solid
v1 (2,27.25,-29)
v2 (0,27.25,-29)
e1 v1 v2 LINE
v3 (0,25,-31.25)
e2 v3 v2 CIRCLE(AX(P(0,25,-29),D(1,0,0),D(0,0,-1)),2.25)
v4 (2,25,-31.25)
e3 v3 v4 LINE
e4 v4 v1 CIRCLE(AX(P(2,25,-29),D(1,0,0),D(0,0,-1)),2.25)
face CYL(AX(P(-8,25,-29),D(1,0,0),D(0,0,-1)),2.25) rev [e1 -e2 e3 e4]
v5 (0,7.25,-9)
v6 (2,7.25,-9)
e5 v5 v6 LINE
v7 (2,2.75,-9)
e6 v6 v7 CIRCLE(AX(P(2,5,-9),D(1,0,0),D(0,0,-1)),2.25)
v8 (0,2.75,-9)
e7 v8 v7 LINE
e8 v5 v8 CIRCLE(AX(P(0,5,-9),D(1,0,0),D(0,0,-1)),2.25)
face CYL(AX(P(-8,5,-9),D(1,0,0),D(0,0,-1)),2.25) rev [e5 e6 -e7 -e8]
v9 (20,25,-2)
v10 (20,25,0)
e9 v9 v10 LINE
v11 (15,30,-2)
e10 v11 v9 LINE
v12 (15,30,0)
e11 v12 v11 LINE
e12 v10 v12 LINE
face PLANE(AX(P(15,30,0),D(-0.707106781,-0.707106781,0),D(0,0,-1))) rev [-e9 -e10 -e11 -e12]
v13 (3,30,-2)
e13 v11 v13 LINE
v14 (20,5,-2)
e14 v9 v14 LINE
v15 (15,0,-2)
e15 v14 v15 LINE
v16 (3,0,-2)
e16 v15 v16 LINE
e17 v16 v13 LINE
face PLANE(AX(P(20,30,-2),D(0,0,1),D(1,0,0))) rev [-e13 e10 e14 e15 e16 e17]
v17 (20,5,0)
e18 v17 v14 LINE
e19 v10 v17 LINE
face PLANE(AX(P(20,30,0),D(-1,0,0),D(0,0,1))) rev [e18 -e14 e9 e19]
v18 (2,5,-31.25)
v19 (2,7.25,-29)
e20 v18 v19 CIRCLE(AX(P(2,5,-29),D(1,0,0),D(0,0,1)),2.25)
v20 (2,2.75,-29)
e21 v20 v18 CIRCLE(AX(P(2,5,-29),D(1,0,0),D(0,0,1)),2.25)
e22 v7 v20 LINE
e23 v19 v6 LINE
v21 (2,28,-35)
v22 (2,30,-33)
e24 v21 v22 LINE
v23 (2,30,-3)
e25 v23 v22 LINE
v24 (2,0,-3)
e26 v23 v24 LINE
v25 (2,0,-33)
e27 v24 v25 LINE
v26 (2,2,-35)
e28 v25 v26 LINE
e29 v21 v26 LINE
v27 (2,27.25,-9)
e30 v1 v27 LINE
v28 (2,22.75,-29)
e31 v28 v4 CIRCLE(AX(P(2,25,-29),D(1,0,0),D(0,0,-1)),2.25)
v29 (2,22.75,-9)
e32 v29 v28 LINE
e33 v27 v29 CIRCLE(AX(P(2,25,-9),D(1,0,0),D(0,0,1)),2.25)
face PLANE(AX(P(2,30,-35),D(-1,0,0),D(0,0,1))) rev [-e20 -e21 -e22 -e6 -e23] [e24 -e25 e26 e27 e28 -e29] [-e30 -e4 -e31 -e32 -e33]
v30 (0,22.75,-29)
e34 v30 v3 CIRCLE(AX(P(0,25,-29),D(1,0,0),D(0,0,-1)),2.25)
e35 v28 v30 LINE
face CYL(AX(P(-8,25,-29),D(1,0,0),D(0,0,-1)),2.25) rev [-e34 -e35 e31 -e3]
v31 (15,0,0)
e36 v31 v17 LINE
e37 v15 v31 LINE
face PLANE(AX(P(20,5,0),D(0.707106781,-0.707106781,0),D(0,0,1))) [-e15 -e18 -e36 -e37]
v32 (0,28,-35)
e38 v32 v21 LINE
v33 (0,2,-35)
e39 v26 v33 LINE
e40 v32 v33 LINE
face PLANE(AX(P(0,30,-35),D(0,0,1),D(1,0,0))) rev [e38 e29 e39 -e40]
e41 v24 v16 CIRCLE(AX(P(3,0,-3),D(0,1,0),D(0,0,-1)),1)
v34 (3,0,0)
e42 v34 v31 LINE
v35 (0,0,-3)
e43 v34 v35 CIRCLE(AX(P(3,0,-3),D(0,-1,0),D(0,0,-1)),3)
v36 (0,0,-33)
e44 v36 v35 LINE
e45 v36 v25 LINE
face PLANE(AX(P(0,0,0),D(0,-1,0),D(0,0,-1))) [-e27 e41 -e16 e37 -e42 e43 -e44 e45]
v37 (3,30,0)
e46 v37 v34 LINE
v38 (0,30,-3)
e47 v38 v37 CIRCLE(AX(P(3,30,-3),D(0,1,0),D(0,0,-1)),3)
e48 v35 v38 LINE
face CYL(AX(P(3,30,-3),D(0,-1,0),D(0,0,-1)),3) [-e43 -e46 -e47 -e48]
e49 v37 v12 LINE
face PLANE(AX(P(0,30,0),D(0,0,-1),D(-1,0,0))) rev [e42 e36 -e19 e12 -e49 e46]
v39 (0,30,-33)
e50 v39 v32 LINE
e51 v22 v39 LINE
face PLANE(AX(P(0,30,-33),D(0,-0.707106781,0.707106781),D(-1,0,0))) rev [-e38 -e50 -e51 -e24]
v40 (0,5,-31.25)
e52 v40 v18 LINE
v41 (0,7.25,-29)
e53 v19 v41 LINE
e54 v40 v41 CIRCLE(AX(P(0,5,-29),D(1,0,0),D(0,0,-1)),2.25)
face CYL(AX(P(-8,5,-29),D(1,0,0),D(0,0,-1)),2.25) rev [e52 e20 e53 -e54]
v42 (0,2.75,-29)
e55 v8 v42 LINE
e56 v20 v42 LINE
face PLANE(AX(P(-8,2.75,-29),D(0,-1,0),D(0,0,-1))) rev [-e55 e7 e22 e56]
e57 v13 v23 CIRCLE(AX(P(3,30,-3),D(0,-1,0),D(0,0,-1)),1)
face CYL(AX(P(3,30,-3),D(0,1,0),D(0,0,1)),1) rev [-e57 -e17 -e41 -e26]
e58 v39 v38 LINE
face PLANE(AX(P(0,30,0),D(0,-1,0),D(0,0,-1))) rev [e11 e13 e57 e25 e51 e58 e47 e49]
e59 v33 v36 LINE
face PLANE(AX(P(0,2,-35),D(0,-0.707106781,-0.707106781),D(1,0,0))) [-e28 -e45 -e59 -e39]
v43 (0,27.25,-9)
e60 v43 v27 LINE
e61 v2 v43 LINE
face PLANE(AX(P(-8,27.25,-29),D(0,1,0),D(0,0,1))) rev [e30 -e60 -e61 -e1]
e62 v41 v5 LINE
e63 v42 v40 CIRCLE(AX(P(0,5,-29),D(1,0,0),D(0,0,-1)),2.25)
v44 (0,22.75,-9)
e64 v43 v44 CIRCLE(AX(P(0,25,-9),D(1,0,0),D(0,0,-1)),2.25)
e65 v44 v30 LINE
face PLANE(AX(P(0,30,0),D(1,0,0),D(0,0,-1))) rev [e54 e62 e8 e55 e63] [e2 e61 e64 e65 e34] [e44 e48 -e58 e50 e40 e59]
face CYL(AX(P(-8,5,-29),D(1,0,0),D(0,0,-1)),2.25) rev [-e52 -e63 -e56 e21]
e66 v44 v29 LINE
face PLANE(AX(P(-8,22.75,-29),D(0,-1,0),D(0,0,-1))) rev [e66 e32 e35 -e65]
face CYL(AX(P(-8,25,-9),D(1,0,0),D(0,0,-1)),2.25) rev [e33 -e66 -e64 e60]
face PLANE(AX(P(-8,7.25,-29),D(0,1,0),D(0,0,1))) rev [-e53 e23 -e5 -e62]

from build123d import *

# Parameters (mm, degrees)
BOSS_EXTRUDE1_DEPTH = 30
SKETCH3_R           = 2.25
CUT_EXTRUDE2_DEPTH  = 10
CHAMFER2_SIZE       = 2
FILLET1_R           = 1
FILLET2_R           = 3
CHAMFER3_SIZE       = 5
CUT_EXTRUDE3_DEPTH  = 10


with BuildPart() as part:
    # Sketch1 → Boss-Extrude1 (new body)
    with BuildSketch(Plane(origin=(0, 0, 0), x_dir=(1, 0, 0), z_dir=(0, 1, 0))):
        Polygon((0, 0), (20, 0), (20, 2), (2, 2), (2, 35), (0, 35), align=None)
    extrude(amount=BOSS_EXTRUDE1_DEPTH)

    # Sketch3 → Cut-Extrude2 (cut)
    with BuildSketch(Plane(origin=(2, 0, 0), x_dir=(0, 0, -1), z_dir=(1, 0, 0))):
        with Locations((29, 25)):
            Circle(SKETCH3_R)
        with Locations((29, 5)):
            Circle(SKETCH3_R)
    extrude(amount=-CUT_EXTRUDE2_DEPTH, mode=Mode.SUBTRACT)

    # Chamfer2
    chamfer2_edges = [part.edges().sort_by_distance(p)[0] for p in [
        (1, 30, -35),
        (1, 0, -35),
    ]]
    chamfer(chamfer2_edges, length=CHAMFER2_SIZE)

    # Fillet1
    fillet1_edges = [part.edges().sort_by_distance(p)[0] for p in [
        (2, 15, -2),
    ]]
    fillet(fillet1_edges, radius=FILLET1_R)

    # Fillet2
    fillet2_edges = [part.edges().sort_by_distance(p)[0] for p in [
        (0, 15, 0),
    ]]
    fillet(fillet2_edges, radius=FILLET2_R)

    # Chamfer3
    chamfer3_edges = [part.edges().sort_by_distance(p)[0] for p in [
        (20, 30, -1),
        (20, 0, -1),
    ]]
    chamfer(chamfer3_edges, length=CHAMFER3_SIZE)

    # Sketch4 → Cut-Extrude3 (cut)
    with BuildSketch(Plane(origin=(2, 0, 0), x_dir=(0, 0, -1), z_dir=(1, 0, 0))):
        with BuildLine():
            Line((29, 2.75), (9, 2.75))
            ThreePointArc((9, 2.75), (6.75, 5), (9, 7.25))
            Line((9, 7.25), (29, 7.25))
            ThreePointArc((29, 7.25), (31.25, 5), (29, 2.75))
        make_face()
        with BuildLine():
            Line((29, 27.25), (9, 27.25))
            ThreePointArc((9, 27.25), (6.75, 25), (9, 22.75))
            Line((9, 22.75), (29, 22.75))
            ThreePointArc((29, 22.75), (31.25, 25), (29, 27.25))
        make_face()
    extrude(amount=-CUT_EXTRUDE3_DEPTH, mode=Mode.SUBTRACT)


solid = part.part
